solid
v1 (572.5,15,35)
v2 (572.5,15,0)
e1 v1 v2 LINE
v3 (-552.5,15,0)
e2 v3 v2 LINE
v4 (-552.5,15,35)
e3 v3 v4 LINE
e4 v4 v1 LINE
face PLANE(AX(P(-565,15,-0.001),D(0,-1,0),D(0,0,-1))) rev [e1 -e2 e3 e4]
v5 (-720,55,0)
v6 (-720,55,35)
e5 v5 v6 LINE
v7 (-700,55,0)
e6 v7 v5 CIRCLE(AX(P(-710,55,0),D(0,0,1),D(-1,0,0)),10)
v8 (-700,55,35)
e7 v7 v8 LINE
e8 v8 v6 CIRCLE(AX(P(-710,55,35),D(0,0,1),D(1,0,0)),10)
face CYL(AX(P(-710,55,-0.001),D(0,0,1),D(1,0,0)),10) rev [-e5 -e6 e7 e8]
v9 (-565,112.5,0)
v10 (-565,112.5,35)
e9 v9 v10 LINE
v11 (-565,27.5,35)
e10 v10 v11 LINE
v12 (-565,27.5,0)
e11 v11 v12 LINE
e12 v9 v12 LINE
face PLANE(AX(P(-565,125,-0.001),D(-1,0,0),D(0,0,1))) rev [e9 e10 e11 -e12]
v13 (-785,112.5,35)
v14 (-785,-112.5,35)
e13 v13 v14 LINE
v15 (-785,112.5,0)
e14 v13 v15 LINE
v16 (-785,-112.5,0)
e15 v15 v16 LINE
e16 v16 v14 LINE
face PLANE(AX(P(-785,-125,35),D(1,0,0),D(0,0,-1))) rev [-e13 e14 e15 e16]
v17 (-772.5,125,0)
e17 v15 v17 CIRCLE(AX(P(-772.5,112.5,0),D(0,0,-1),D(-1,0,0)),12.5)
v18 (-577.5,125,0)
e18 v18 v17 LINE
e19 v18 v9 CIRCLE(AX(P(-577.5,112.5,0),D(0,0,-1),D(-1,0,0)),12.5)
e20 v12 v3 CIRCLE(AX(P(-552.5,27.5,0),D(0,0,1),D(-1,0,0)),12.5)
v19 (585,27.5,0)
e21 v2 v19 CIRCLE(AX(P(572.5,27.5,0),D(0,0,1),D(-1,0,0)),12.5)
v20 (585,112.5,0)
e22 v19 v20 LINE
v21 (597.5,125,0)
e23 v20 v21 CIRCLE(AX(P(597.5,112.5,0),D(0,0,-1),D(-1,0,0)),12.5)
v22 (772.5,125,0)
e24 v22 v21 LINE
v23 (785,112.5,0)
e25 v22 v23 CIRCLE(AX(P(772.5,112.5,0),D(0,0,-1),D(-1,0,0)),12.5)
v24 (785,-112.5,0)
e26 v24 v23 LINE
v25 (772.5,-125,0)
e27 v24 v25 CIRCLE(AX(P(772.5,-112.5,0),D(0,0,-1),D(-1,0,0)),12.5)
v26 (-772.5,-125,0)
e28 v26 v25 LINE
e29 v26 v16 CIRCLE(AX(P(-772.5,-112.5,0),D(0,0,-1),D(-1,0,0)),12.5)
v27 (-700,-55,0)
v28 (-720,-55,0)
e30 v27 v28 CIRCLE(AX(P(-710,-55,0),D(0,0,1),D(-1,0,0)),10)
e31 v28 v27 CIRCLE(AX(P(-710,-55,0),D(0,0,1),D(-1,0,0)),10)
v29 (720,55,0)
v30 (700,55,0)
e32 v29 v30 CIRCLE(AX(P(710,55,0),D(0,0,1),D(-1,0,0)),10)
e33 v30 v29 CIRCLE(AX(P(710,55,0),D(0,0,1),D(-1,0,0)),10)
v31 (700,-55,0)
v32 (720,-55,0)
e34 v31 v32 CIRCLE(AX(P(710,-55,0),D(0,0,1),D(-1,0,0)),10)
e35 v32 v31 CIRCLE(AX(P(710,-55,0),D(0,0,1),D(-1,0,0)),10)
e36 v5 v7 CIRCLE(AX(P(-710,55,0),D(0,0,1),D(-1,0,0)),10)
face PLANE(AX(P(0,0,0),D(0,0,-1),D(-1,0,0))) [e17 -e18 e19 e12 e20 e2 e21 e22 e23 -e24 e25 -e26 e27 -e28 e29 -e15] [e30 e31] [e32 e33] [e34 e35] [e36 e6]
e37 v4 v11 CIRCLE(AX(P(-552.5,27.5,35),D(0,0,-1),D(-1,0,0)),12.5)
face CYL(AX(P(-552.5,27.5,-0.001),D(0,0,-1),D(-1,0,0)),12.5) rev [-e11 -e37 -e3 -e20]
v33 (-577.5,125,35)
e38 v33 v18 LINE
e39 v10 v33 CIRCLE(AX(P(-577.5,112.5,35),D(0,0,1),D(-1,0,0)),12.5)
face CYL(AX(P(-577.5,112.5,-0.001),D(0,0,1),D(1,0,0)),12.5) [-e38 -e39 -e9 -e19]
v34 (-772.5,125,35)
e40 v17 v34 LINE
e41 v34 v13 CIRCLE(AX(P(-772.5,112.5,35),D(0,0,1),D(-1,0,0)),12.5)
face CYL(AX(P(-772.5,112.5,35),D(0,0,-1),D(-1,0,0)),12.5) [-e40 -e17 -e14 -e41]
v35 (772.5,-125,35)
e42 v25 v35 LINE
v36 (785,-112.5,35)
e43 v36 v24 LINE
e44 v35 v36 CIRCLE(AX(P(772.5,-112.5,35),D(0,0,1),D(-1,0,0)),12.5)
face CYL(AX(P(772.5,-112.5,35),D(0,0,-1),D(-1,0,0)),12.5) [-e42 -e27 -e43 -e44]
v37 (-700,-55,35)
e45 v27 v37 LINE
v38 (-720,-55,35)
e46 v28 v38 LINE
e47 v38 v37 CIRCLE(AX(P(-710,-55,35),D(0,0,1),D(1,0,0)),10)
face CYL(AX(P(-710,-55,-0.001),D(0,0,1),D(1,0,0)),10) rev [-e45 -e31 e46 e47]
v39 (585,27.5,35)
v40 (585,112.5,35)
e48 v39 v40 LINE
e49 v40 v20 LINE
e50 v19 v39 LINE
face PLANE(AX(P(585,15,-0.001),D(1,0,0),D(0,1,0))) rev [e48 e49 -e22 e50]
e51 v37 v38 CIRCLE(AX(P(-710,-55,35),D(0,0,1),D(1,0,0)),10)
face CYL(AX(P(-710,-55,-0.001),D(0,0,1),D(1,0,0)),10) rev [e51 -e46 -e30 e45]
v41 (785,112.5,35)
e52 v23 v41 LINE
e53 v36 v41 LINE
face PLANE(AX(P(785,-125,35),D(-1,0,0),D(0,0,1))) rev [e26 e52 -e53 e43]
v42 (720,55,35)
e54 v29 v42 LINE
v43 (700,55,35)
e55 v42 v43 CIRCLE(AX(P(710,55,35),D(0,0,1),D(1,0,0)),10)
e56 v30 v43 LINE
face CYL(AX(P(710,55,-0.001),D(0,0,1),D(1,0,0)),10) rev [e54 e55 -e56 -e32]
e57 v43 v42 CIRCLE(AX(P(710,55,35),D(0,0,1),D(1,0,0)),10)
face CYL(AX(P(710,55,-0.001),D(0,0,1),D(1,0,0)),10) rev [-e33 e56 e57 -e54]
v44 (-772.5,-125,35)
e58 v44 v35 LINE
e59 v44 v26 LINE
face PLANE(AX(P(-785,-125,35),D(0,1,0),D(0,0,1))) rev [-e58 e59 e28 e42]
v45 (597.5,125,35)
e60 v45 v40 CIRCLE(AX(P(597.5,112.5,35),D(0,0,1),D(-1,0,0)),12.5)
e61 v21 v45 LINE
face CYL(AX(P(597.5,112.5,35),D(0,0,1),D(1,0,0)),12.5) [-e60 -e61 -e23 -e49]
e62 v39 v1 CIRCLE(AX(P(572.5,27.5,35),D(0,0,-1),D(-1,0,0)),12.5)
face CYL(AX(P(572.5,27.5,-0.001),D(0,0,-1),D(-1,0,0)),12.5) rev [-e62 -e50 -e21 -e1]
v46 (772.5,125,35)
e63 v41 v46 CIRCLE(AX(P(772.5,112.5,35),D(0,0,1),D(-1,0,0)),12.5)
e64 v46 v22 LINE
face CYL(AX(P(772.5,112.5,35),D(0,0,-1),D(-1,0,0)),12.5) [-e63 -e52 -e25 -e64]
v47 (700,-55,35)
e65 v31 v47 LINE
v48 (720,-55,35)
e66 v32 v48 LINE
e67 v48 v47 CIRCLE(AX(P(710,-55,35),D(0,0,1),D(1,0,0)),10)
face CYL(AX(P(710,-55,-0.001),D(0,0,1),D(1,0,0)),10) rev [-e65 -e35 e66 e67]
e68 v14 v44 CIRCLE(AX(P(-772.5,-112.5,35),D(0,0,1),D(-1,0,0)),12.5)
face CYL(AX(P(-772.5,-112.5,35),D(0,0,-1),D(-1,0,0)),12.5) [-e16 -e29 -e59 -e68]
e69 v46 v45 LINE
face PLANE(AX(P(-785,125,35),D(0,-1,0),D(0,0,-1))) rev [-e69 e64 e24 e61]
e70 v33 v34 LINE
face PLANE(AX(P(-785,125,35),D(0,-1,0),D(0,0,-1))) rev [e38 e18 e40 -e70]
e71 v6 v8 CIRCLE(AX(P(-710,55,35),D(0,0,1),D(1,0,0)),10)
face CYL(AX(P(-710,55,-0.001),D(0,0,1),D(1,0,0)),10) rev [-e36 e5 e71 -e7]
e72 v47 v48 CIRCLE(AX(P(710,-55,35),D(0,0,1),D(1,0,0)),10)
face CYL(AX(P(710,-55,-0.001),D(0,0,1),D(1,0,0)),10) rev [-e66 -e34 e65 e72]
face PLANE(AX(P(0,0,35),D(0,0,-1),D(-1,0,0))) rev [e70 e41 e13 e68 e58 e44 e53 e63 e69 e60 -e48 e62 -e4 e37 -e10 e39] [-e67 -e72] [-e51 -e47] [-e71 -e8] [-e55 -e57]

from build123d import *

# Parameters (mm, degrees)
SKETCH_1_W          = 1570
SKETCH_1_H          = 250
EXTRUDE_1_DEPTH     = 35
CUT_EXTRUDE_1_REACH = 797.66
SKETCH_2_W          = 1150
SKETCH_2_H          = 110
FILLET_1_R          = 12.5
CUT_EXTRUDE_2_REACH = 797.66
SKETCH_4_R          = 10


with BuildPart() as part:
    # 草图1 → 凸台-拉伸1 (new body)
    with BuildSketch(Plane.XY):
        Rectangle(SKETCH_1_W, SKETCH_1_H)
    extrude(amount=EXTRUDE_1_DEPTH)

    # 草图2 → 切除-拉伸1 (cut, up to next)
    with BuildSketch(Plane.XY.offset(35), mode=Mode.PRIVATE) as cut_extrude_1_sk1:
        with Locations((10, 70)):
            Rectangle(SKETCH_2_W, SKETCH_2_H)
    cut_extrude_1_tool1 = extrude(cut_extrude_1_sk1.sketch, amount=-CUT_EXTRUDE_1_REACH, mode=Mode.PRIVATE) & part.part
    add(cut_extrude_1_tool1.solids().sort_by_distance((10, 70, 35))[0], mode=Mode.SUBTRACT)

    # 圆角1
    fillet_1_edges = [part.edges().sort_by_distance(p)[0] for p in [
        (-565, 125, 17.5),
        (585, 125, 17.5),
        (585, 15, 17.5),
        (-565, 15, 17.5),
        (785, -125, 17.5),
        (-785, -125, 17.5),
        (-785, 125, 17.5),
        (785, 125, 17.5),
    ]]
    fillet(fillet_1_edges, radius=FILLET_1_R)

    # 草图4 → 切除-拉伸2 (cut, up to next)
    with BuildSketch(Plane.XY.offset(35), mode=Mode.PRIVATE) as cut_extrude_2_sk1:
        with Locations((-710, 55)):
            Circle(SKETCH_4_R)
    cut_extrude_2_tool1 = extrude(cut_extrude_2_sk1.sketch, amount=-CUT_EXTRUDE_2_REACH, mode=Mode.PRIVATE) & part.part
    # 草图4 → 切除-拉伸2 (cut, up to next)
    with BuildSketch(Plane.XY.offset(35), mode=Mode.PRIVATE) as cut_extrude_2_sk2:
        with Locations((-710, -55)):
            Circle(SKETCH_4_R)
    cut_extrude_2_tool2 = extrude(cut_extrude_2_sk2.sketch, amount=-CUT_EXTRUDE_2_REACH, mode=Mode.PRIVATE) & part.part
    # 草图4 → 切除-拉伸2 (cut, up to next)
    with BuildSketch(Plane.XY.offset(35), mode=Mode.PRIVATE) as cut_extrude_2_sk3:
        with Locations((710, 55)):
            Circle(SKETCH_4_R)
    cut_extrude_2_tool3 = extrude(cut_extrude_2_sk3.sketch, amount=-CUT_EXTRUDE_2_REACH, mode=Mode.PRIVATE) & part.part
    # 草图4 → 切除-拉伸2 (cut, up to next)
    with BuildSketch(Plane.XY.offset(35), mode=Mode.PRIVATE) as cut_extrude_2_sk4:
        with Locations((710, -55)):
            Circle(SKETCH_4_R)
    cut_extrude_2_tool4 = extrude(cut_extrude_2_sk4.sketch, amount=-CUT_EXTRUDE_2_REACH, mode=Mode.PRIVATE) & part.part
    add(cut_extrude_2_tool1.solids().sort_by_distance((-710, 55, 35))[0], mode=Mode.SUBTRACT)
    add(cut_extrude_2_tool2.solids().sort_by_distance((-710, -55, 35))[0], mode=Mode.SUBTRACT)
    add(cut_extrude_2_tool3.solids().sort_by_distance((710, 55, 35))[0], mode=Mode.SUBTRACT)
    add(cut_extrude_2_tool4.solids().sort_by_distance((710, -55, 35))[0], mode=Mode.SUBTRACT)


solid = part.part
